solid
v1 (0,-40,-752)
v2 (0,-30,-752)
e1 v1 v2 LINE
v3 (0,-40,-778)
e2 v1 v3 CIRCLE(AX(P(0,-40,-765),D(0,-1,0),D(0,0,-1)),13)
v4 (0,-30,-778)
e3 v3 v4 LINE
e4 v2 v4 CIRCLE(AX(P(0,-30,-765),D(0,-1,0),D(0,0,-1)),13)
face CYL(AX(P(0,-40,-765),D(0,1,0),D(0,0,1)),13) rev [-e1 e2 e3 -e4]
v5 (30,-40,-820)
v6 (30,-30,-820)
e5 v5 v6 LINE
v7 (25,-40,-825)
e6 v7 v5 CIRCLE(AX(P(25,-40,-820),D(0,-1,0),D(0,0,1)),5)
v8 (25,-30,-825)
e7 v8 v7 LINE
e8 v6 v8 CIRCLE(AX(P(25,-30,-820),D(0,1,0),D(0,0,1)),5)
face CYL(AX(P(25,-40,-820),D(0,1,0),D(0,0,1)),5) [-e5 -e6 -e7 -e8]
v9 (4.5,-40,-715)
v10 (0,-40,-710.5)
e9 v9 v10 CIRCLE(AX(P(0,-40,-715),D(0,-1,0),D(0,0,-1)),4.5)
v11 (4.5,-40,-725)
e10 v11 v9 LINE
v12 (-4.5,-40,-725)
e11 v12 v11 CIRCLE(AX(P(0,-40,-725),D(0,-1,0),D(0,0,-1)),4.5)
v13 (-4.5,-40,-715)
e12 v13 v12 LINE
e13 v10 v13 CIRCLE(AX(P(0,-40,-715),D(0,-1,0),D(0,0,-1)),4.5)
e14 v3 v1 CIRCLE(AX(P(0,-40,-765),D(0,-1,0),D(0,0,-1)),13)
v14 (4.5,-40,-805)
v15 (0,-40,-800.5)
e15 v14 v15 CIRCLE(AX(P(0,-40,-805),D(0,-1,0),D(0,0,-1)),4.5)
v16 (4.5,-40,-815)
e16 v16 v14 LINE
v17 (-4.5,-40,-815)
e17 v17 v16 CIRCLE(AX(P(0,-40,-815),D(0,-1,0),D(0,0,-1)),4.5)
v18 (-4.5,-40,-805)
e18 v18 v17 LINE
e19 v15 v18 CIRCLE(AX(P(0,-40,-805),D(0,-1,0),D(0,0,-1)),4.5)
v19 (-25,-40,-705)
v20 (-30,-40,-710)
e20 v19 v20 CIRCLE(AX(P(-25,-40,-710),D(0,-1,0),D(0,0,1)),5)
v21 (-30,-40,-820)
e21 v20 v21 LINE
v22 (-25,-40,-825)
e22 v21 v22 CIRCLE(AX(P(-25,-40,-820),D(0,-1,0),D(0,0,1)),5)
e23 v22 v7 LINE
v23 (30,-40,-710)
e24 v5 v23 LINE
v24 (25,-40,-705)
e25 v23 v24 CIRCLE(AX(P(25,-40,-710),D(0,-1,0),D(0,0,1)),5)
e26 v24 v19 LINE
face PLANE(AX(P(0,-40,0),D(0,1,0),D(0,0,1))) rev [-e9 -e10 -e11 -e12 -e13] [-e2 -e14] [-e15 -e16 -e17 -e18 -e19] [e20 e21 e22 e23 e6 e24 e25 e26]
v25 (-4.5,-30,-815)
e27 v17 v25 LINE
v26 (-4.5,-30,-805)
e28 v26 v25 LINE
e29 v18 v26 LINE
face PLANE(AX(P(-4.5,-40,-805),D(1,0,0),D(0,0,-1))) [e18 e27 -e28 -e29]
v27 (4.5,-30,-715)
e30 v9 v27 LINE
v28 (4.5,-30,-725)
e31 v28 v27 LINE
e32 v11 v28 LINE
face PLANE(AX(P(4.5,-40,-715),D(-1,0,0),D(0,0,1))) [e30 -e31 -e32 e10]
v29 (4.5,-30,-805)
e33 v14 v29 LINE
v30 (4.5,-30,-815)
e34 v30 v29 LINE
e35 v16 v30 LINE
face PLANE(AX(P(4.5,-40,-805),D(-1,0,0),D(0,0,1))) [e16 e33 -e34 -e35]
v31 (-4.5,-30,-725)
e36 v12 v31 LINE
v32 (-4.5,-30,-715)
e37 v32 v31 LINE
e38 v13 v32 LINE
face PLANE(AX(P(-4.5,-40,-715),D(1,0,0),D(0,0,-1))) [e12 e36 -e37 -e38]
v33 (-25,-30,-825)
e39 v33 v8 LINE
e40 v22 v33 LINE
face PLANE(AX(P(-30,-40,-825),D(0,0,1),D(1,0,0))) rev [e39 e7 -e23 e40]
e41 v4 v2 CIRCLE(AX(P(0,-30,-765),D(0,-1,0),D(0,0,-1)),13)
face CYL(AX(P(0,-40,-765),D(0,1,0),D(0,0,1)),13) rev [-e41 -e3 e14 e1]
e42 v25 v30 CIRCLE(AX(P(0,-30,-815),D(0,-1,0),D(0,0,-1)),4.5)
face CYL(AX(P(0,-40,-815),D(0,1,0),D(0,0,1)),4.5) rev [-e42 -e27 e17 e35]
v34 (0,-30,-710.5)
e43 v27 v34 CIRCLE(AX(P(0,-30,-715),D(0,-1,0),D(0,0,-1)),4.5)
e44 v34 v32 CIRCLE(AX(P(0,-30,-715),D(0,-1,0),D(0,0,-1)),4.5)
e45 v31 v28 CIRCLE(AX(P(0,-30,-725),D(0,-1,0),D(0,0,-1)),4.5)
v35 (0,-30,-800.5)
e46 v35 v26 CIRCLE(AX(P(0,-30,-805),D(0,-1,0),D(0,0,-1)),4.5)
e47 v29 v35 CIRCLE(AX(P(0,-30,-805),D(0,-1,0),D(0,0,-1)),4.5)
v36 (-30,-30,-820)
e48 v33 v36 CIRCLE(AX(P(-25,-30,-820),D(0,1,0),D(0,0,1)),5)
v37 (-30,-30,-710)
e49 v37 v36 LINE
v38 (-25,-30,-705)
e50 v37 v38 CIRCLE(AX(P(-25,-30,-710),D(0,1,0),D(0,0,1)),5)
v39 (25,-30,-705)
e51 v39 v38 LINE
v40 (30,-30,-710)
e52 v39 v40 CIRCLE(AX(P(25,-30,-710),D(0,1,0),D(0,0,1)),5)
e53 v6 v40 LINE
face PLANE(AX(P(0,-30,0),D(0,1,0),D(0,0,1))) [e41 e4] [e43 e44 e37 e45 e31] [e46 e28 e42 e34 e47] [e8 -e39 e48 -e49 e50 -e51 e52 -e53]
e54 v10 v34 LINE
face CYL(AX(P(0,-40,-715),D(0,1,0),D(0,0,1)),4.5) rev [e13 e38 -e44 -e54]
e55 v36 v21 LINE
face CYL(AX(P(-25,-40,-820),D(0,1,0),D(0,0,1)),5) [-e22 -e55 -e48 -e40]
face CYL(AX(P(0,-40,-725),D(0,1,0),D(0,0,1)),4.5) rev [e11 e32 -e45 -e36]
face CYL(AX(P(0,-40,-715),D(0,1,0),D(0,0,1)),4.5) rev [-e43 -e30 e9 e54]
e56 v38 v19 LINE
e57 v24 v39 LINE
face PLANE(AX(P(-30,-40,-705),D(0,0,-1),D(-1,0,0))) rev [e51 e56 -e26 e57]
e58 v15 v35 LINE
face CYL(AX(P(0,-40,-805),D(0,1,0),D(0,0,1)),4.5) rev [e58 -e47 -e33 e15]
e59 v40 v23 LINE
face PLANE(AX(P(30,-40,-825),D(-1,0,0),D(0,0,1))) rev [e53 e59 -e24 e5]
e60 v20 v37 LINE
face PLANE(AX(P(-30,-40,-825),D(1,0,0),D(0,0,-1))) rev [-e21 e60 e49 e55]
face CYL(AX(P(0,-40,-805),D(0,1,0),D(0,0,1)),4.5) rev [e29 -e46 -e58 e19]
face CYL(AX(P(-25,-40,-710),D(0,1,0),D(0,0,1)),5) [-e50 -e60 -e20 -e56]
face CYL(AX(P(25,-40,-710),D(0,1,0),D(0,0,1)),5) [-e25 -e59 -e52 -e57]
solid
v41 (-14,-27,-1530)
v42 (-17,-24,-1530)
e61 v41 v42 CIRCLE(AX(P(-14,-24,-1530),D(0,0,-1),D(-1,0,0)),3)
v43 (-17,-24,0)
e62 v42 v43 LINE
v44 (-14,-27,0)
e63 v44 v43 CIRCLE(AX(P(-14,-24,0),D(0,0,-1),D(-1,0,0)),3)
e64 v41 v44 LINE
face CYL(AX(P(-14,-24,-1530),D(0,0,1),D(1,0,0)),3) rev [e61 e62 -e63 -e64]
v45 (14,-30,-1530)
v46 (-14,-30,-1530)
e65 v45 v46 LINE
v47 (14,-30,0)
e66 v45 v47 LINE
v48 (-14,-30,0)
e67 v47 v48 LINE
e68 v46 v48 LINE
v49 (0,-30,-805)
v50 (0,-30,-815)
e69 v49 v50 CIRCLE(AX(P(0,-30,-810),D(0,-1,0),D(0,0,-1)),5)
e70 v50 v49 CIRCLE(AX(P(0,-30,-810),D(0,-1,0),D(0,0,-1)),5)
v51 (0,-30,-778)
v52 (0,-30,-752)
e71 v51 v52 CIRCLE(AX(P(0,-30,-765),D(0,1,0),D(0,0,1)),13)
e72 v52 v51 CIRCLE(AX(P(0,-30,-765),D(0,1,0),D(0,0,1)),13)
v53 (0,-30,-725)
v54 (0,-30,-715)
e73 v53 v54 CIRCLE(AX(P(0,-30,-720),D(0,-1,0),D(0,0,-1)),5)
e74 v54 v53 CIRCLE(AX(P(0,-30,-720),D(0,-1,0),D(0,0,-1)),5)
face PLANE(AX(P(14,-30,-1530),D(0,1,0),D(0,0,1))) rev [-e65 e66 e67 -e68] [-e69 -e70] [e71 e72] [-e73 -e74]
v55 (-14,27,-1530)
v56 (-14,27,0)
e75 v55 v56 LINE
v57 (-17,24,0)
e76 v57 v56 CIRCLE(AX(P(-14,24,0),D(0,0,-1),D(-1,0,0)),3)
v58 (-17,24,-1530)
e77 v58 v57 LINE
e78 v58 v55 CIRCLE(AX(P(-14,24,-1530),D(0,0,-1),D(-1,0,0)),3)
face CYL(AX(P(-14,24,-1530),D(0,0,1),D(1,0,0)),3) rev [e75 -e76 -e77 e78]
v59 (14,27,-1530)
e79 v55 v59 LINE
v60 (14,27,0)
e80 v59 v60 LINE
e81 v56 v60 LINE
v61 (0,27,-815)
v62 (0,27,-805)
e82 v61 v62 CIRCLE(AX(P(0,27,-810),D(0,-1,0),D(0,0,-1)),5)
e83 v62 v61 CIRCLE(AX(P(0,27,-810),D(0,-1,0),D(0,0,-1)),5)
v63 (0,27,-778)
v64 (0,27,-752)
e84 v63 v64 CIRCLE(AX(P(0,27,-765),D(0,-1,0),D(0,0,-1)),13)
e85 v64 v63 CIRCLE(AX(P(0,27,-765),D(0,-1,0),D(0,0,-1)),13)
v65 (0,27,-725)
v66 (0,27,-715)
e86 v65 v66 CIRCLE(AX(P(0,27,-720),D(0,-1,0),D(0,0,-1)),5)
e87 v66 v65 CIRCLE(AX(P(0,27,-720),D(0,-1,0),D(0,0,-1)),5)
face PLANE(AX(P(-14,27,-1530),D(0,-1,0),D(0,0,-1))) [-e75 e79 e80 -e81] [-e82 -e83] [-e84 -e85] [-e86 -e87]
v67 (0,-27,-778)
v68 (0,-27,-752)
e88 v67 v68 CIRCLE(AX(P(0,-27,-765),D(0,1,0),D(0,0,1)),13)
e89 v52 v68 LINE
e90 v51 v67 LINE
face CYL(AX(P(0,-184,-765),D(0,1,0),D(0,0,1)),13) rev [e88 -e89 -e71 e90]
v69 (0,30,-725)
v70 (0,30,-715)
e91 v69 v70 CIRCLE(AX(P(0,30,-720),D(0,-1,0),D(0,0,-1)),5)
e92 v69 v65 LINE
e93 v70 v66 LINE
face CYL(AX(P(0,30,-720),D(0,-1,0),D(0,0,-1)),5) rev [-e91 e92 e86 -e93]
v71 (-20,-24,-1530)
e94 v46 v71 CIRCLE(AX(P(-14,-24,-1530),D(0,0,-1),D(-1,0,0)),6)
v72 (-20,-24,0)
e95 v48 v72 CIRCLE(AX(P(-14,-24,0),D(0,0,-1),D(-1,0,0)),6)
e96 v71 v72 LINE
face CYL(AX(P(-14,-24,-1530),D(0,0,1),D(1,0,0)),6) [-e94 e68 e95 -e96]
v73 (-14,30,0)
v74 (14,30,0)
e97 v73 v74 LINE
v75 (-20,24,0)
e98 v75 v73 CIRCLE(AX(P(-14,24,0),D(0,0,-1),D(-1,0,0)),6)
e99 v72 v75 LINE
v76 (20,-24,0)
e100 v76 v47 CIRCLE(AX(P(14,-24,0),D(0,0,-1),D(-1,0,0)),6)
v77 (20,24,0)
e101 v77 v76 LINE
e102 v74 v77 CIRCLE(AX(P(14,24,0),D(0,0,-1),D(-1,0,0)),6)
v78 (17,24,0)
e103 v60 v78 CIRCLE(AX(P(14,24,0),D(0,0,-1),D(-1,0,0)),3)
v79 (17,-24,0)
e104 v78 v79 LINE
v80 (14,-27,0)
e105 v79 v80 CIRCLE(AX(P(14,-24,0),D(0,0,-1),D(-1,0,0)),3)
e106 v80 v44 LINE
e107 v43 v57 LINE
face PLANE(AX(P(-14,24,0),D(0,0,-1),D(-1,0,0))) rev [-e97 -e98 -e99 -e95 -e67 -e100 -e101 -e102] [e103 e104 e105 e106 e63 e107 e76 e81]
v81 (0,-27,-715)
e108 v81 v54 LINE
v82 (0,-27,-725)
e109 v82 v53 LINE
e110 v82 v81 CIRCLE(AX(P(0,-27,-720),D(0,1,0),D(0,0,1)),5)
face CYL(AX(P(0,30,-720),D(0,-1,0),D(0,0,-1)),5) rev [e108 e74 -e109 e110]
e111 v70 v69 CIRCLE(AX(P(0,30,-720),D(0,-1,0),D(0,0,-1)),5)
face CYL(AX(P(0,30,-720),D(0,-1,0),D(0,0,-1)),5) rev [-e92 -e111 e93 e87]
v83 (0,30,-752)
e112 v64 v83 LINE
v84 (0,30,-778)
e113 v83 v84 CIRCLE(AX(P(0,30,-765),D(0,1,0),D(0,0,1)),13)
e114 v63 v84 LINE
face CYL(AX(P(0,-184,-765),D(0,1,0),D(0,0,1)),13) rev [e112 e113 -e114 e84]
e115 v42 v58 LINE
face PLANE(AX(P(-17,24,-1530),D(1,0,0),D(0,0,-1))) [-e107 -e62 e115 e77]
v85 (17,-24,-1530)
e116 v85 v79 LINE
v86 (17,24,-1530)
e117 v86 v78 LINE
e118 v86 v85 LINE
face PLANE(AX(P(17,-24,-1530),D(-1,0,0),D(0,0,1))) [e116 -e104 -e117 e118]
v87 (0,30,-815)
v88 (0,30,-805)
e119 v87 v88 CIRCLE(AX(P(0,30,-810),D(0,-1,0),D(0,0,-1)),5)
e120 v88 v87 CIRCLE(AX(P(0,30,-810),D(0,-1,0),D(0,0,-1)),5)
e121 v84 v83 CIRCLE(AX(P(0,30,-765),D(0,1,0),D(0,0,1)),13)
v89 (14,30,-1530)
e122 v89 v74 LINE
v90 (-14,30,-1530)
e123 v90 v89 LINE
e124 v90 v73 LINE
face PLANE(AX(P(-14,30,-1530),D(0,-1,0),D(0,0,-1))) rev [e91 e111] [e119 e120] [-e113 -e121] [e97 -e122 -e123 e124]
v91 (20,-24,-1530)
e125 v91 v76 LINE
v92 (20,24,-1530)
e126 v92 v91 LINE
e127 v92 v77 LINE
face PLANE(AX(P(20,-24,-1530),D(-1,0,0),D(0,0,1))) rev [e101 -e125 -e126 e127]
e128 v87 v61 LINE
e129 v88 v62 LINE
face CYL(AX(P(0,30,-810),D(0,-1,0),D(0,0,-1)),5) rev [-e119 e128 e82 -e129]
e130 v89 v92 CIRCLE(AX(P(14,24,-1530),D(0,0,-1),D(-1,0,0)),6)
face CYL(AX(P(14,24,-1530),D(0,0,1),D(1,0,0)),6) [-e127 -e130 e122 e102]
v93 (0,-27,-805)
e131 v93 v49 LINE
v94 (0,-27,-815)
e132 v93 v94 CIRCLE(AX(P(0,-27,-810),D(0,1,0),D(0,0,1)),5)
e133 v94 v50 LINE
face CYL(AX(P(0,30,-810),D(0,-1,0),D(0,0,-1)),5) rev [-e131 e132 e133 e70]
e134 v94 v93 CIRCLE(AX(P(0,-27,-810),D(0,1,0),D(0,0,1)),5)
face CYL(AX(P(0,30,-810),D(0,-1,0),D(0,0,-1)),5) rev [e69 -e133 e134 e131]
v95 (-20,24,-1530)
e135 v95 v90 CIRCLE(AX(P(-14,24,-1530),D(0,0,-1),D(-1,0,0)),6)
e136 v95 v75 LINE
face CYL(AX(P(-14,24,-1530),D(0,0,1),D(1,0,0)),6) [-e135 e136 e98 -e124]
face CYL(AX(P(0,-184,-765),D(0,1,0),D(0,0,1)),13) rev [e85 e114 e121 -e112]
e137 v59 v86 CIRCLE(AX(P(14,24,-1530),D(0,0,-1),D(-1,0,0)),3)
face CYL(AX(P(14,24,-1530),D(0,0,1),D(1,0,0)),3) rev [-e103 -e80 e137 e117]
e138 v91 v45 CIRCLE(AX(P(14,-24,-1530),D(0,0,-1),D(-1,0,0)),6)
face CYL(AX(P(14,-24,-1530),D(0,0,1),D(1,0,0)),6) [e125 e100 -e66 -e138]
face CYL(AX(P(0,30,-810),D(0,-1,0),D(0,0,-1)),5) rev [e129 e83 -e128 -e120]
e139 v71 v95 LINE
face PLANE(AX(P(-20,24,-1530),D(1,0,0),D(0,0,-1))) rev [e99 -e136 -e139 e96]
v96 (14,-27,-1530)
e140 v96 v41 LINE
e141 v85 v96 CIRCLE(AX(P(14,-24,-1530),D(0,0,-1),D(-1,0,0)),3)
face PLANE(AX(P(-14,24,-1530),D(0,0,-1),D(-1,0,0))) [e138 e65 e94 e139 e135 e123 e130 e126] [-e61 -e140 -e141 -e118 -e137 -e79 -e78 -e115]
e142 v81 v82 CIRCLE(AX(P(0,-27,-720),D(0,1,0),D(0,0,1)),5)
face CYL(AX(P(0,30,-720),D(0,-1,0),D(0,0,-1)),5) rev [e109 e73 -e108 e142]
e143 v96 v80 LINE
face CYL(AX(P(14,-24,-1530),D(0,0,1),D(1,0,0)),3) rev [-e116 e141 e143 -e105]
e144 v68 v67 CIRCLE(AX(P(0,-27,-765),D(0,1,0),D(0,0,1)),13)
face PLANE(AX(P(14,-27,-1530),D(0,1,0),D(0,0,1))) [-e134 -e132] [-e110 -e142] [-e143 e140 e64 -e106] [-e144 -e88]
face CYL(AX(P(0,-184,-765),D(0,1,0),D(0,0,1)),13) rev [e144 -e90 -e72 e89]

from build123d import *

# Parameters (mm, degrees)
GB_6728_1986_RECTANGULAR_HOLLOW_SECTION_DEPTH = 1530
SKETCH5_R                                     = 13
CUT_EXTRUDE1_DEPTH                            = 214
SKETCH6_W                                     = 60
SKETCH6_H                                     = 120
SKETCH6_R                                     = 13
BOSS_EXTRUDE1_DEPTH                           = 10
SKETCH7_R                                     = 5
CUT_EXTRUDE2_DEPTH                            = 1532.469882172
FILLET1_R                                     = 5


with BuildPart() as part:
    # Sketch14 → Gb/6728-1986 rectangular hollow section 060 X 40 X 3 (new body)
    with BuildSketch(Plane(origin=(0, 0, 0), x_dir=(-1, 0, 0), z_dir=(0, 0, -1))):
        with BuildLine():
            Line((-14, -30), (14, -30))
            ThreePointArc((14, -30), (18.242640687, -28.242640687), (20, -24))
            Line((20, -24), (20, 24))
            ThreePointArc((20, 24), (18.242640687, 28.242640687), (14, 30))
            Line((14, 30), (-14, 30))
            ThreePointArc((-14, 30), (-18.242640687, 28.242640687), (-20, 24))
            Line((-20, 24), (-20, -24))
            ThreePointArc((-20, -24), (-18.242640687, -28.242640687), (-14, -30))
        make_face()
        with BuildLine():
            Line((-14, -27), (14, -27))
            ThreePointArc((14, -27), (16.121320344, -26.121320344), (17, -24))
            Line((17, -24), (17, 24))
            ThreePointArc((17, 24), (16.121320344, 26.121320344), (14, 27))
            Line((14, 27), (-14, 27))
            ThreePointArc((-14, 27), (-16.121320344, 26.121320344), (-17, 24))
            Line((-17, 24), (-17, -24))
            ThreePointArc((-17, -24), (-16.121320344, -26.121320344), (-14, -27))
        make_face(mode=Mode.SUBTRACT)
    extrude(amount=GB_6728_1986_RECTANGULAR_HOLLOW_SECTION_DEPTH)

    # Sketch5 → Cut-Extrude1 (cut)
    with BuildSketch(Plane(origin=(0, 30, 0), x_dir=(1, 0, 0), z_dir=(0, 1, 0))):
        with Locations(Location((0, 765, 0), (0, 0, 270))):
            Circle(SKETCH5_R)
    extrude(amount=-CUT_EXTRUDE1_DEPTH, mode=Mode.SUBTRACT)

    # Sketch7 → Cut-Extrude2 (cut, through all)
    with BuildSketch(Plane.XZ.offset(30)):
        with Locations(Location((0, -720, 0), (0, 0, 270))):
            Circle(SKETCH7_R)
        with Locations(Location((0, -810, 0), (0, 0, 270))):
            Circle(SKETCH7_R)
    extrude(amount=-CUT_EXTRUDE2_DEPTH, mode=Mode.SUBTRACT)


with BuildPart() as body_2:
    # Sketch6 → Boss-Extrude1 (new body)
    with BuildSketch(Plane.XZ.offset(30)):
        with Locations((0, -765)):
            Rectangle(SKETCH6_W, SKETCH6_H)
        with Locations(Location((0, -765, 0), (0, 0, 270))):
            Circle(SKETCH6_R, mode=Mode.SUBTRACT)
        with BuildLine():
            Line((4.5, -715), (4.5, -725))
            ThreePointArc((4.5, -725), (0, -729.5), (-4.5, -725))
            Line((-4.5, -725), (-4.5, -715))
            ThreePointArc((-4.5, -715), (0, -710.5), (4.5, -715))
        make_face(mode=Mode.SUBTRACT)
        with BuildLine():
            Line((4.5, -805), (4.5, -815))
            ThreePointArc((4.5, -815), (0, -819.5), (-4.5, -815))
            Line((-4.5, -815), (-4.5, -805))
            ThreePointArc((-4.5, -805), (0, -800.5), (4.5, -805))
        make_face(mode=Mode.SUBTRACT)
    extrude(amount=BOSS_EXTRUDE1_DEPTH)

    # Fillet1
    fillet1_edges = [body_2.edges().sort_by_distance(p)[0] for p in [
        (30, -35, -825),
        (-30, -35, -825),
        (-30, -35, -705),
        (30, -35, -705),
    ]]
    fillet(fillet1_edges, radius=FILLET1_R)


solid = Compound([part.part, body_2.part])
